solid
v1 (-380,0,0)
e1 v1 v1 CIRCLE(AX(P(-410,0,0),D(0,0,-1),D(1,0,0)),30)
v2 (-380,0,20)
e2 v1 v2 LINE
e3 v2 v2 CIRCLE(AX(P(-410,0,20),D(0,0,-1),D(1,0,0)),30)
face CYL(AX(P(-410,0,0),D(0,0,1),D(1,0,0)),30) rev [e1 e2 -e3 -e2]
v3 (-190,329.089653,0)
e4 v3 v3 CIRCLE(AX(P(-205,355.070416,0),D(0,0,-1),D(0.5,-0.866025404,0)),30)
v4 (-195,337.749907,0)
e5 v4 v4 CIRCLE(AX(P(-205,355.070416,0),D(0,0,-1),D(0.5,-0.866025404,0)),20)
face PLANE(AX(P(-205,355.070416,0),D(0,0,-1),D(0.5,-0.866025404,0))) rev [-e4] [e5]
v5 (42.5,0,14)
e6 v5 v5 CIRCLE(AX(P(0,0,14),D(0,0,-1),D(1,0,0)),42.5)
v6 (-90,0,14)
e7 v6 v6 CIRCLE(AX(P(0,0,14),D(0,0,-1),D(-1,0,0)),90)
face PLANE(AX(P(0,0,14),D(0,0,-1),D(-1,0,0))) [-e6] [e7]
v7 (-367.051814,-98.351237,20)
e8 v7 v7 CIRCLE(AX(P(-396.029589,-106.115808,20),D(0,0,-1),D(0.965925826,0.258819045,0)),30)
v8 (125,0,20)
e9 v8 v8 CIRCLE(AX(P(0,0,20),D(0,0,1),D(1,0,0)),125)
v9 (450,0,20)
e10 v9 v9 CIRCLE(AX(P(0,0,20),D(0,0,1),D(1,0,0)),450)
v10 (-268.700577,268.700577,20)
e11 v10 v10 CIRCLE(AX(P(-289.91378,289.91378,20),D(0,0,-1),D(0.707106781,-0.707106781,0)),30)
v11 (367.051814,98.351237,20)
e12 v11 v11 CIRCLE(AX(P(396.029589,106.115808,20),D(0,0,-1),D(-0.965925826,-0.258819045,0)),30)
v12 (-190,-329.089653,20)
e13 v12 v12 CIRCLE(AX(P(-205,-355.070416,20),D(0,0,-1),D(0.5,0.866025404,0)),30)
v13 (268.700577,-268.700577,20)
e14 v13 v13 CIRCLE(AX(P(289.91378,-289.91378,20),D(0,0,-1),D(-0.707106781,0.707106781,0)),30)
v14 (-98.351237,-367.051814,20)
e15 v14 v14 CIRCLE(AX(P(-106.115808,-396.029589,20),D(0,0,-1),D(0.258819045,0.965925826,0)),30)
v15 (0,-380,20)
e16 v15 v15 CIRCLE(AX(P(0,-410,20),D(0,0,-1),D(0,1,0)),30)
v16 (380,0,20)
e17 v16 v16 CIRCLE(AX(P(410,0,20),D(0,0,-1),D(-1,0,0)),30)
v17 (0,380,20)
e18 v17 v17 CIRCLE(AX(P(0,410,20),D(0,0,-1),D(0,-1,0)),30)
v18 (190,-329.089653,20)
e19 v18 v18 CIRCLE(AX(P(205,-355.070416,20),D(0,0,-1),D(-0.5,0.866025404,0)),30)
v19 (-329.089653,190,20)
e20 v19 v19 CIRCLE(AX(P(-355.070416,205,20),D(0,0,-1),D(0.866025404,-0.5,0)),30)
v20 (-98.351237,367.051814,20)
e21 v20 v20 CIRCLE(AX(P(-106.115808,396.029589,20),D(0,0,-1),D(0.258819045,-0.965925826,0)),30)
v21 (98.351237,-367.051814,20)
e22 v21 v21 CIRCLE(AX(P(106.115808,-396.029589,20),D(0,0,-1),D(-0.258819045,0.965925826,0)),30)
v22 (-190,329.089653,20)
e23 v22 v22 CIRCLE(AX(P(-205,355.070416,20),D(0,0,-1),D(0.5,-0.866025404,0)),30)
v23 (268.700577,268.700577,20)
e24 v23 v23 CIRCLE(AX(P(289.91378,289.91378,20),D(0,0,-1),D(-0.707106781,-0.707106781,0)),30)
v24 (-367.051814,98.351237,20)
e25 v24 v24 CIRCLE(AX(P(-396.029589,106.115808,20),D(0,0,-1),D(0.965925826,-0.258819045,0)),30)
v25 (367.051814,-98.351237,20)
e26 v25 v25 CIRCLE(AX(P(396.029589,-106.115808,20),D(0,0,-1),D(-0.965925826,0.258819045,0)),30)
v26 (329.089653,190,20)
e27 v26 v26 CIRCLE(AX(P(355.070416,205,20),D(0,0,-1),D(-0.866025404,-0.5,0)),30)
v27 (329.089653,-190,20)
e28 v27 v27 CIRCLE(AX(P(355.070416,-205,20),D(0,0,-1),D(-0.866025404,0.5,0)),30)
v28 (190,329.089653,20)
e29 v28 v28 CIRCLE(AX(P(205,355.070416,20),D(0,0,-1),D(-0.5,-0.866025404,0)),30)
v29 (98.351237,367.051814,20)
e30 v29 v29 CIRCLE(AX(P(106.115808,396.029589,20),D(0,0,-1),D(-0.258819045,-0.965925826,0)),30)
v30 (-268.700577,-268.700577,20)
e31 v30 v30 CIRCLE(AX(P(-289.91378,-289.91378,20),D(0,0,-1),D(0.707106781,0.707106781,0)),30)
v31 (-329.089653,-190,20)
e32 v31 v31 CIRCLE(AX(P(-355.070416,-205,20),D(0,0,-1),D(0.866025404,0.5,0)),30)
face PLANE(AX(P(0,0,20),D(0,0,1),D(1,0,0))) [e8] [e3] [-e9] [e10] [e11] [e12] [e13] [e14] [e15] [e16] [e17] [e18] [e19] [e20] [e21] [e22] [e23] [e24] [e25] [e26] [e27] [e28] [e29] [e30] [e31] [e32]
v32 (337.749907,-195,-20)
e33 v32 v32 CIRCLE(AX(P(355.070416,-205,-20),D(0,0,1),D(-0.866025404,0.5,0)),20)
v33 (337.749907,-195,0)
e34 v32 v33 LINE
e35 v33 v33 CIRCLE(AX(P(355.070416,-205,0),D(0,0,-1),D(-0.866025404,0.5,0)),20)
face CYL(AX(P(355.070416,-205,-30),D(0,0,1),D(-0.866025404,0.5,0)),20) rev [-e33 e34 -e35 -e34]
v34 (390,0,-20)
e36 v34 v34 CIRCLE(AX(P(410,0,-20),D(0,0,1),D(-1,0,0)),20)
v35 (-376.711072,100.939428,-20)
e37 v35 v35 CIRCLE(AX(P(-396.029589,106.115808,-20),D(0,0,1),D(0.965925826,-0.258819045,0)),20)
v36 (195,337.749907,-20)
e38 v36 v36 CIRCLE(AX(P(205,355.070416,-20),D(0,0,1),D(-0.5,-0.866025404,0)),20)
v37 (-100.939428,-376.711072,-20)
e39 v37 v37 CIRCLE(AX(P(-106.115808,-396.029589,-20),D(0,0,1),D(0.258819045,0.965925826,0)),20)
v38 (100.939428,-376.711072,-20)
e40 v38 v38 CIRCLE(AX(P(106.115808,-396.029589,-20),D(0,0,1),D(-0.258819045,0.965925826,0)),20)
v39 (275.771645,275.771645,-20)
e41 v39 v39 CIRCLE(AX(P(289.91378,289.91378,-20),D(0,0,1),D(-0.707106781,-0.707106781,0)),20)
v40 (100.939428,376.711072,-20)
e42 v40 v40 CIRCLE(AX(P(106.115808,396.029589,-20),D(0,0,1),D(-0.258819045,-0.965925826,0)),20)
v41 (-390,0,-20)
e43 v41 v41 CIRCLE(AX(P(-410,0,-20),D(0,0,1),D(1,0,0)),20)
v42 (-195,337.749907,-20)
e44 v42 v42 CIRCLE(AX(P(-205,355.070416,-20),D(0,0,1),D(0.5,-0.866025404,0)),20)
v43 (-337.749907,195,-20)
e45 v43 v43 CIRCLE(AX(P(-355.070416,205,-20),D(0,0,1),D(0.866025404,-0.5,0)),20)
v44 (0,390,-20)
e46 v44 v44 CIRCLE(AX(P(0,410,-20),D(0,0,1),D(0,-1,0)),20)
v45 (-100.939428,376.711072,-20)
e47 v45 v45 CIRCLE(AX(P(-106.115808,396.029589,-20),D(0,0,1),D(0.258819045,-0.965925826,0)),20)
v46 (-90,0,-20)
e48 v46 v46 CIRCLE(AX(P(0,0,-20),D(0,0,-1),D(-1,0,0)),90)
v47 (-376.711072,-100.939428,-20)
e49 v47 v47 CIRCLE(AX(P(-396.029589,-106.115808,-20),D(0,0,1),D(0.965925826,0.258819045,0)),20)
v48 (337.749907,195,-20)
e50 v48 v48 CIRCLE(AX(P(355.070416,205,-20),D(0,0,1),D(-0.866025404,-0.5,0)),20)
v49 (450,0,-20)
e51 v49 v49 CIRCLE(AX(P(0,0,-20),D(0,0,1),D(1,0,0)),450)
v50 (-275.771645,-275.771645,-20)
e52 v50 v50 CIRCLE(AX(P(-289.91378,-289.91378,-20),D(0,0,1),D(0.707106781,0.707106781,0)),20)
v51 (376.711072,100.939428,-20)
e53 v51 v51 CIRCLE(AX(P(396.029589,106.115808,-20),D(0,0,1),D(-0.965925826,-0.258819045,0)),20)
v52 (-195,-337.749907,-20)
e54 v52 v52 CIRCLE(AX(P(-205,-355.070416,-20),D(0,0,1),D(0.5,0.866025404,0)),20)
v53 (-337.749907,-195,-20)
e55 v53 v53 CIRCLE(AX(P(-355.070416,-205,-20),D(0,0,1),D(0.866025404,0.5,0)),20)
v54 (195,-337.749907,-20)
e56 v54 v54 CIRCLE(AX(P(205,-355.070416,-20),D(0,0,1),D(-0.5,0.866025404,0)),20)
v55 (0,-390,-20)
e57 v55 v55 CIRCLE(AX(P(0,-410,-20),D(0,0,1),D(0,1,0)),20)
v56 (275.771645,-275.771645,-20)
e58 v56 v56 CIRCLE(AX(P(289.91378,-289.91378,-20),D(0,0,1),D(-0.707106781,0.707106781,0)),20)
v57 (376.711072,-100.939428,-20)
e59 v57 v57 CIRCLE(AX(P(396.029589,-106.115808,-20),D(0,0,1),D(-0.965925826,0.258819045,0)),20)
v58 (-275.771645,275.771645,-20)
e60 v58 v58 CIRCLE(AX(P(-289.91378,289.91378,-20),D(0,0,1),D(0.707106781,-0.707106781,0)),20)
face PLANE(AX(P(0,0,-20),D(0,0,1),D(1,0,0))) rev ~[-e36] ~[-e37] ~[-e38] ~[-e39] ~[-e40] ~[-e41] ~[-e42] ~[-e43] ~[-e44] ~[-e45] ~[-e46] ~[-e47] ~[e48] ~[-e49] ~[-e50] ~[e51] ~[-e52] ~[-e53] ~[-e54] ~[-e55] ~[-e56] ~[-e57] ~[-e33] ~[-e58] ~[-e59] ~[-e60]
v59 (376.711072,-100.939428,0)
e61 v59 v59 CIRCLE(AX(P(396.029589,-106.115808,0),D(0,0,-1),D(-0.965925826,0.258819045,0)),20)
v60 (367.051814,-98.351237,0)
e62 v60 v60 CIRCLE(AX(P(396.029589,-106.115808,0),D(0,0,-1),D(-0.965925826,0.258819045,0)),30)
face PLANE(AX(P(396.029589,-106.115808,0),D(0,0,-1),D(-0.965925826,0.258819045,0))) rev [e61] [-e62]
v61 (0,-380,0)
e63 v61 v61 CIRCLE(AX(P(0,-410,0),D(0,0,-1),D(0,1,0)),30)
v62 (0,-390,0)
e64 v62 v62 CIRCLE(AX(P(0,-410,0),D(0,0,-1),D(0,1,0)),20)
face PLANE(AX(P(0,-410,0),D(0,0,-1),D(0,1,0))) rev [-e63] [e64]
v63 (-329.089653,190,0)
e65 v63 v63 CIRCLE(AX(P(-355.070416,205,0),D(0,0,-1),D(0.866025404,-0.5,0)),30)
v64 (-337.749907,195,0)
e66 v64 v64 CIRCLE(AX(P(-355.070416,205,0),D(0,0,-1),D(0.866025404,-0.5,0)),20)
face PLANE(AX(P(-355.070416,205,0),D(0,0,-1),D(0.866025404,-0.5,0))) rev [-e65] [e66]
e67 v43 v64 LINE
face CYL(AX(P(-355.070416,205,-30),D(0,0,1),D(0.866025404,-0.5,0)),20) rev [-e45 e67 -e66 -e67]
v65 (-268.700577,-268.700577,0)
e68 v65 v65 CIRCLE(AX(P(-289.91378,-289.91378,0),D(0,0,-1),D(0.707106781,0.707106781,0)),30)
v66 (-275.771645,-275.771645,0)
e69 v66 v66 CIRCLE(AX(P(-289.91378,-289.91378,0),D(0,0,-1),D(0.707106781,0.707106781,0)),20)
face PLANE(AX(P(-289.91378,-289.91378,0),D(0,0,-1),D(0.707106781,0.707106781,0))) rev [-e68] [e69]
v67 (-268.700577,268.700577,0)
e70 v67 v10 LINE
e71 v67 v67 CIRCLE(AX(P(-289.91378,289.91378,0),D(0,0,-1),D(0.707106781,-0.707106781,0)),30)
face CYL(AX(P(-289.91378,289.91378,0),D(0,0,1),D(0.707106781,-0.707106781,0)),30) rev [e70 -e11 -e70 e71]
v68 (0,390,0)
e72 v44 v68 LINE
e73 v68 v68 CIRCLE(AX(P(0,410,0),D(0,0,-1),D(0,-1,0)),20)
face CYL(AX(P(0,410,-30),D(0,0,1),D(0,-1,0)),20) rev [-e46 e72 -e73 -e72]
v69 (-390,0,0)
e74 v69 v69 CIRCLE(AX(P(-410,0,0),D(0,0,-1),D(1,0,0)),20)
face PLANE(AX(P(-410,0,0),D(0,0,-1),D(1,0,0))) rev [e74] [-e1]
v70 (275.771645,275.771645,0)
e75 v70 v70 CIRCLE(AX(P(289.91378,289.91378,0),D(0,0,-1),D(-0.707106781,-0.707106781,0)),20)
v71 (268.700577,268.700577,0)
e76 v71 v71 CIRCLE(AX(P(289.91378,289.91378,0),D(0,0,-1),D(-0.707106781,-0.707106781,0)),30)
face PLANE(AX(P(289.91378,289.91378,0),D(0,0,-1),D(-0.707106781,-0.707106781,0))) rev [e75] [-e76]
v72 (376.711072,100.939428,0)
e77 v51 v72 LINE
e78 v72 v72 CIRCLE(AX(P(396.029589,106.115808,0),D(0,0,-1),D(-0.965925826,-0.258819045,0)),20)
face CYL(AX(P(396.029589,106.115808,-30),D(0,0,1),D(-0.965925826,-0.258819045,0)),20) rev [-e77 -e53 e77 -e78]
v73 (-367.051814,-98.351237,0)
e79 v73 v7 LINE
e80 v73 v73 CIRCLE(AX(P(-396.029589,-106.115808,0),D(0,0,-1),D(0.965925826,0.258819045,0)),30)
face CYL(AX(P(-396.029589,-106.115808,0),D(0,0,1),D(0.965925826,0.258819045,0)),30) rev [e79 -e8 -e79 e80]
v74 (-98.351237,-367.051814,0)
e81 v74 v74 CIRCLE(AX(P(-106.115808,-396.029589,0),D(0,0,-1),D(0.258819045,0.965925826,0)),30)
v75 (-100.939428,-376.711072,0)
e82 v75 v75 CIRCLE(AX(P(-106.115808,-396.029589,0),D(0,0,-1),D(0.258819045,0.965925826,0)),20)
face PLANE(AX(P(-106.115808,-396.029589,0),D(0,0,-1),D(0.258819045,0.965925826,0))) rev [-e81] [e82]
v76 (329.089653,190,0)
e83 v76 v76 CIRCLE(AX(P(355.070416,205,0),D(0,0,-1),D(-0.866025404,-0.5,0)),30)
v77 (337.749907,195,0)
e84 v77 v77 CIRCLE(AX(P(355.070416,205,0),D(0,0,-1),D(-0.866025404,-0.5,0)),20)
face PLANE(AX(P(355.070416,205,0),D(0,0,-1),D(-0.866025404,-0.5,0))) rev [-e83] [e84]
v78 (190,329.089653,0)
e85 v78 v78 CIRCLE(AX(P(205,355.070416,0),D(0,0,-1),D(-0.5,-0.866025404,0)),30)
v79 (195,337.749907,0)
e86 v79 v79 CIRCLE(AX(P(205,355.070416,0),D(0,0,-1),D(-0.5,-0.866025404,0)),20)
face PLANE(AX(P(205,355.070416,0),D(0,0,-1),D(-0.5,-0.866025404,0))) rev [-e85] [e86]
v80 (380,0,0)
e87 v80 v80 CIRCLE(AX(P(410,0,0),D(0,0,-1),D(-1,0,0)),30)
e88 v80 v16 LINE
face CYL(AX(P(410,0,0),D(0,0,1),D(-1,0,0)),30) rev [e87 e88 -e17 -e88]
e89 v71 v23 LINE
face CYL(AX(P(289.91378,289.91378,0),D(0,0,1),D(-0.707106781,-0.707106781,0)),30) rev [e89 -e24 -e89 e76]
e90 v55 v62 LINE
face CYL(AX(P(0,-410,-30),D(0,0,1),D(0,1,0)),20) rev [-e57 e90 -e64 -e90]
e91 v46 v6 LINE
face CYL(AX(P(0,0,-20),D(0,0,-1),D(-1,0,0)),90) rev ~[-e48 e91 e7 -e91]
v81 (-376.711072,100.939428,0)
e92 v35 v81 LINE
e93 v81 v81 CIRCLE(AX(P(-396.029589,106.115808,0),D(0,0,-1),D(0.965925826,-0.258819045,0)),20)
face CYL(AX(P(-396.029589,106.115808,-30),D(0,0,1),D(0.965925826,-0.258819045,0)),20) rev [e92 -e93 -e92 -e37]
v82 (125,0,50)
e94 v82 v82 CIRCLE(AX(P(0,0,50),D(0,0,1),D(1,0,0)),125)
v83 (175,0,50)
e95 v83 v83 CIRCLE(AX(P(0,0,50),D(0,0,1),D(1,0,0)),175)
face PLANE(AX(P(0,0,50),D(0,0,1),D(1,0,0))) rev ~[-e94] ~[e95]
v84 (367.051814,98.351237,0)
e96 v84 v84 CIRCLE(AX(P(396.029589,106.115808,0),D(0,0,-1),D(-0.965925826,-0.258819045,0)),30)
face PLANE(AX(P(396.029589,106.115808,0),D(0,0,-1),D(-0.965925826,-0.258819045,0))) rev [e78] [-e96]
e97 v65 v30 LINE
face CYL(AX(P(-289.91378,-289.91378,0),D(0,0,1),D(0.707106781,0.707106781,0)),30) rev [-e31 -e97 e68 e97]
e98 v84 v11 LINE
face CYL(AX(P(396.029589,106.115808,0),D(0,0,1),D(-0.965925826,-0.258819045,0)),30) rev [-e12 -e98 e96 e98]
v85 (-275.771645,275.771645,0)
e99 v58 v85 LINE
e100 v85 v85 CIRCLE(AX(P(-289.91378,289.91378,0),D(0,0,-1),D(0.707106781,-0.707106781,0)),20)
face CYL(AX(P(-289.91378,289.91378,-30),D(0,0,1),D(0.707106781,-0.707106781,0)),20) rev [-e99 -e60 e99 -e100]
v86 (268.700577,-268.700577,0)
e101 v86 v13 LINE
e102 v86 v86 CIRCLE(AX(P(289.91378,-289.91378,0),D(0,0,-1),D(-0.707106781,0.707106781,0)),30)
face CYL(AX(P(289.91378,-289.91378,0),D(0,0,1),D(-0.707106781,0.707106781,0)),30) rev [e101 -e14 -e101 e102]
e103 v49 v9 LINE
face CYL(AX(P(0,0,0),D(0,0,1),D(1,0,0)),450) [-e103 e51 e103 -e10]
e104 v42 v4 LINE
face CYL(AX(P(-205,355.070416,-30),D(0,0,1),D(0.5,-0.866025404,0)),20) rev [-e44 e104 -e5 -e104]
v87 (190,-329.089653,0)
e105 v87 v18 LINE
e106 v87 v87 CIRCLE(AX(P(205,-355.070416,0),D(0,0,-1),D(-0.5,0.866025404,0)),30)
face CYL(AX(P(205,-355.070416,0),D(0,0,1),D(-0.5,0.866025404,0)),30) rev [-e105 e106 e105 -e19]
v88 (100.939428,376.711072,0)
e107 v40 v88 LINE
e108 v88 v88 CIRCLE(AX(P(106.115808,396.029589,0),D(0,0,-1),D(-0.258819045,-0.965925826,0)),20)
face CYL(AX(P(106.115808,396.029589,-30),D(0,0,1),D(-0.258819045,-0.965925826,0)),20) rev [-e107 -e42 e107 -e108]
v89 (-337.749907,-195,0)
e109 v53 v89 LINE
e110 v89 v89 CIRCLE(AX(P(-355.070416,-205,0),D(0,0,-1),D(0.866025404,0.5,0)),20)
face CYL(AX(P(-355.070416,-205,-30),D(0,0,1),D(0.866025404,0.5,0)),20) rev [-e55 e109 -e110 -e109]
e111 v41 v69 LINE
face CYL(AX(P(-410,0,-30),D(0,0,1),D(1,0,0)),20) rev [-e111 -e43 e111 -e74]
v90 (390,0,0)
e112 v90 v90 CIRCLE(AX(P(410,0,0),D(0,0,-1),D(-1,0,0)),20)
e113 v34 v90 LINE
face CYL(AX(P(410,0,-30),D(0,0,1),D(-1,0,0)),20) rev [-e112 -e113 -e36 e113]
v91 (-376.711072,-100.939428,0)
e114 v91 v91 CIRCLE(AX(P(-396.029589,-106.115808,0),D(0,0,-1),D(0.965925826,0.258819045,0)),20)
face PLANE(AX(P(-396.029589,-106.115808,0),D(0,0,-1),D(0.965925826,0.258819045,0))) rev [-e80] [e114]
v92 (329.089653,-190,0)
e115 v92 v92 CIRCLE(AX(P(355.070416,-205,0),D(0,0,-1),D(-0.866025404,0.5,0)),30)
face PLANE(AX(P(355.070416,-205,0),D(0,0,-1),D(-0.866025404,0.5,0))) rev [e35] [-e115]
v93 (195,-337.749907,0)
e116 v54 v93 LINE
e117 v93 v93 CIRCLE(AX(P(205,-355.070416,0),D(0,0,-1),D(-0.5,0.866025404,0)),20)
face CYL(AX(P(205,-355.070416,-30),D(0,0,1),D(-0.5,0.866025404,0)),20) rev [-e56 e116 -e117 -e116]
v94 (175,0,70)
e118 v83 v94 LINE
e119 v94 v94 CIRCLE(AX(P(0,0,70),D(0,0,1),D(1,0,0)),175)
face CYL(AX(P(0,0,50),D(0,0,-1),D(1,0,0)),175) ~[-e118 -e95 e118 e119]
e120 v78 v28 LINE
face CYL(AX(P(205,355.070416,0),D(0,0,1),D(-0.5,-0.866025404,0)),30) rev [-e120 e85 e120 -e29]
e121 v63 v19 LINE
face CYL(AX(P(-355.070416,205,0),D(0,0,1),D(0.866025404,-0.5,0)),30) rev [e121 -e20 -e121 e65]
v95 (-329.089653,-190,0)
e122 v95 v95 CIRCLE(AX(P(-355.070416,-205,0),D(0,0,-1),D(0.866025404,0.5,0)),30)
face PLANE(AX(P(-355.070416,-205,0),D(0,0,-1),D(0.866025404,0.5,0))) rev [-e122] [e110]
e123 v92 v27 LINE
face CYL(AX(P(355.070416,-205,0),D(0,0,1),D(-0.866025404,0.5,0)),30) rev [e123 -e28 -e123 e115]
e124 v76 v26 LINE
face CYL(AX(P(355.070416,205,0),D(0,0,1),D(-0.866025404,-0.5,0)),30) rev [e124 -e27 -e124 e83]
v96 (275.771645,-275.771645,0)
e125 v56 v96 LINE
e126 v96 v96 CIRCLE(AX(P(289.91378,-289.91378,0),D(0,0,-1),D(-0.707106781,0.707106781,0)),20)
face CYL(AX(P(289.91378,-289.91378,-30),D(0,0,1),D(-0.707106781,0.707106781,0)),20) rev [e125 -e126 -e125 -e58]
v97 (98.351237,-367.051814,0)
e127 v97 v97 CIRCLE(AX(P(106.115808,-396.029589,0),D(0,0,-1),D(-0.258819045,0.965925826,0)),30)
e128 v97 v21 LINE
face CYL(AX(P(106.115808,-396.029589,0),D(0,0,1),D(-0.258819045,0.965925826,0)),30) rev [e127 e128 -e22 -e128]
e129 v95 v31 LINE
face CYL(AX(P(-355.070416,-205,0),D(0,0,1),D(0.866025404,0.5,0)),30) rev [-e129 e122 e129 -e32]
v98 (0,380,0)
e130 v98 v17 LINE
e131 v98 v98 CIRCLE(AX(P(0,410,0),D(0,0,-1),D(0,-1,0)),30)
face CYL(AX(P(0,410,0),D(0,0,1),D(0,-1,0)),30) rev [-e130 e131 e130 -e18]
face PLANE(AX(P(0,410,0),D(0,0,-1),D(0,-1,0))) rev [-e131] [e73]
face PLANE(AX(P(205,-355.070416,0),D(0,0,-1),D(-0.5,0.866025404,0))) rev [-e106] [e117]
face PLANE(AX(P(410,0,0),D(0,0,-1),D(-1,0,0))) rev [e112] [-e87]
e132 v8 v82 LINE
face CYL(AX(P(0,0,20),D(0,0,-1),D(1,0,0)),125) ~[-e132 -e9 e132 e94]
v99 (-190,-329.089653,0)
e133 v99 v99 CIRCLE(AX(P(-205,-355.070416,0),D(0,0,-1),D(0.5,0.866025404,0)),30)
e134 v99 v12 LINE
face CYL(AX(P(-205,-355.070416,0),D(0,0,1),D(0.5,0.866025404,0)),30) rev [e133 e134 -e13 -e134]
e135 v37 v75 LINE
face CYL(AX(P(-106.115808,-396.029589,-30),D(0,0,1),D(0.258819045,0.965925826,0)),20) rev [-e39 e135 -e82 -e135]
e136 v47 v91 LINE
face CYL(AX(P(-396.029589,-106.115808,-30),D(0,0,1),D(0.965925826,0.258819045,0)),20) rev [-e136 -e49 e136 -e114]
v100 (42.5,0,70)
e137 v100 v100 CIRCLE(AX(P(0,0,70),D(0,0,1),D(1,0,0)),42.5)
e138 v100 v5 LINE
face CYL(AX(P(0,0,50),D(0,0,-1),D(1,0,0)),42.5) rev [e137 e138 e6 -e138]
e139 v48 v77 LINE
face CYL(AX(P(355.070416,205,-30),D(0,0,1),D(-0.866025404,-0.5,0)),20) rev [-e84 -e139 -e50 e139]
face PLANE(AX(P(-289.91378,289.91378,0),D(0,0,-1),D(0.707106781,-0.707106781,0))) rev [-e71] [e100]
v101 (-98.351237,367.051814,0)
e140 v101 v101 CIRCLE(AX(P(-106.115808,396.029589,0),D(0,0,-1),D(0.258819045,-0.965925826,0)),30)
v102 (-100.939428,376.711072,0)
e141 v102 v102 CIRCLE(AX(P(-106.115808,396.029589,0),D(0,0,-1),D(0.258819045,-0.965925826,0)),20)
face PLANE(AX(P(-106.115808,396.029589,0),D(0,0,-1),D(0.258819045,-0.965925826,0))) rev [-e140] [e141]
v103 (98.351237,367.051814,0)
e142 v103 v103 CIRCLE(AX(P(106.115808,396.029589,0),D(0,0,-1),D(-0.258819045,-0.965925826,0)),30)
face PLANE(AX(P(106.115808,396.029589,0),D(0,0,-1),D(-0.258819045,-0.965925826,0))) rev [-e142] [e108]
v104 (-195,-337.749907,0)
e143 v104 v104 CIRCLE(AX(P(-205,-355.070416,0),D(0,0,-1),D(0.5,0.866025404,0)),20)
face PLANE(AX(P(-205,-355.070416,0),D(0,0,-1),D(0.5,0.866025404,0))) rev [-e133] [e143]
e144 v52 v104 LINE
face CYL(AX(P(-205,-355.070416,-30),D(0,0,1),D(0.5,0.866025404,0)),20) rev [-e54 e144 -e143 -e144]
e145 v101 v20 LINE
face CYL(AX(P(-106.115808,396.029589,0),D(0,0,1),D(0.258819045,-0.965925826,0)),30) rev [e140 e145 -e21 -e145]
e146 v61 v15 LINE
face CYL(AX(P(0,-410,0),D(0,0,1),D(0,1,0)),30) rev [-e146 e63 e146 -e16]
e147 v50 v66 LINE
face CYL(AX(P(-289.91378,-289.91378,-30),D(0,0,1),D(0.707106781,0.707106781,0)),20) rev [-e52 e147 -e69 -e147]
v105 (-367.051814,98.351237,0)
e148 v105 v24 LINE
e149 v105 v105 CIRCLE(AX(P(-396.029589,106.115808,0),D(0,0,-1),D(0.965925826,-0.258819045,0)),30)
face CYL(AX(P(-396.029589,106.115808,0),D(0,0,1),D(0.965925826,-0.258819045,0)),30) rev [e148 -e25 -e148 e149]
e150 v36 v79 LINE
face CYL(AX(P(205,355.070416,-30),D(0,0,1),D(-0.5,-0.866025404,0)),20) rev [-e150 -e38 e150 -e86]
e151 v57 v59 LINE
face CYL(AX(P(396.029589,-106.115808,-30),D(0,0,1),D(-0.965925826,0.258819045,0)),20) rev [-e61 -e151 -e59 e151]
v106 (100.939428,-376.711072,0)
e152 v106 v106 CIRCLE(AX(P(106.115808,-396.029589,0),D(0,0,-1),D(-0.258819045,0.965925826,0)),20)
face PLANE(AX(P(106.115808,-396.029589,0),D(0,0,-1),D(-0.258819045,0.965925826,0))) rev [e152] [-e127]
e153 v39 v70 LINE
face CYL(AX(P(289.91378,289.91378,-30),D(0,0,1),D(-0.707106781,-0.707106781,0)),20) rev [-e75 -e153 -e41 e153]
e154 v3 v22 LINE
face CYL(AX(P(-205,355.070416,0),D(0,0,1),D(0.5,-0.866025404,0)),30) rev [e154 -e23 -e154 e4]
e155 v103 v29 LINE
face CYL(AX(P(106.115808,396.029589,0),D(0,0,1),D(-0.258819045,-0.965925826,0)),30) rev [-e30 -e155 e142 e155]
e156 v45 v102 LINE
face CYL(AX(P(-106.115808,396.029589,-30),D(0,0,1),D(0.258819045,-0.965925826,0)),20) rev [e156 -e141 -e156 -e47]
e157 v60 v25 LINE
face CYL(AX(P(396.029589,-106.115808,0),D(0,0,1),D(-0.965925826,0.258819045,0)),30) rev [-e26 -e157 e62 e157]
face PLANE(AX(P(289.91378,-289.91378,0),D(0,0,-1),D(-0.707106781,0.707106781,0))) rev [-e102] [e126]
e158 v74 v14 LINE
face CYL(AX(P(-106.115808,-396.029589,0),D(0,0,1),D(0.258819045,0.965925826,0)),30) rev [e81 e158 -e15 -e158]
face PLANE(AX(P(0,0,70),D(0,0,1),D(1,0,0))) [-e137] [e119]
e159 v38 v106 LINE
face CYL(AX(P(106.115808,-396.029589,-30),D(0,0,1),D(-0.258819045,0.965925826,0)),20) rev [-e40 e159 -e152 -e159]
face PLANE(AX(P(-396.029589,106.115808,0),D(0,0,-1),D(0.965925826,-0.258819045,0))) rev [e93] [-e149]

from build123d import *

# Parameters (mm, degrees)
SKETCH_1_R               = 450
SKETCH_1_R_2             = 42.5
EXTRUDE_1_DEPTH          = 20
PATTERN_CIRCULAR_1_COUNT = 24
SKETCH_7_R               = 125
SKETCH_7_R_2             = 42.5
EXTRUDE_2_DEPTH          = 30
SKETCH_8_R               = 175
SKETCH_8_R_2             = 42.5
EXTRUDE_3_DEPTH          = 20
SKETCH_9_R               = 90
CUT_EXTRUDE_1_DEPTH      = 34


with BuildPart() as part:
    # 草图1 → 凸台-拉伸1 (new, symmetric)
    with BuildSketch(Plane.XY):
        Circle(SKETCH_1_R)
        Circle(SKETCH_1_R_2, mode=Mode.SUBTRACT)
    extrude(amount=EXTRUDE_1_DEPTH, both=True)

    # 草图4 → M42 六角头螺栓的柱形沉头孔1 (revolve, cut)
    with BuildSketch(Plane(origin=(0, 410, 20), x_dir=(0, -1, 0), z_dir=(1, 0, 0))):
        Polygon((0, 0), (0, 62.017212381), (20, 50), (20, 20), (30, 20), (30, 0), align=None)
    hole_wizard_m42_1 = revolve(axis=Axis((0, 410, 26.35), (0, 0, -1)), mode=Mode.SUBTRACT)

    # 阵列(圆周)1: M42 六角头螺栓的柱形沉头孔1 ×24 about axis
    pattern_circular_1_axis = Axis((0, 0, 0), (0, 0, 1))
    for i in range(1, PATTERN_CIRCULAR_1_COUNT):
        add(hole_wizard_m42_1.rotate(pattern_circular_1_axis, i * 360 / PATTERN_CIRCULAR_1_COUNT), mode=Mode.SUBTRACT)

    # 草图7 → 凸台-拉伸2 (add)
    with BuildSketch(Plane.XY.offset(20)):
        Circle(SKETCH_7_R)
        Circle(SKETCH_7_R_2, mode=Mode.SUBTRACT)
    extrude(amount=EXTRUDE_2_DEPTH)

    # 草图8 → 凸台-拉伸3 (add)
    with BuildSketch(Plane.XY.offset(50)):
        Circle(SKETCH_8_R)
        Circle(SKETCH_8_R_2, mode=Mode.SUBTRACT)
    extrude(amount=EXTRUDE_3_DEPTH)

    # 草图9 → 切除-拉伸1 (cut)
    with BuildSketch(Plane(origin=(0, 0, -20), x_dir=(-1, 0, 0), z_dir=(0, 0, -1))):
        Circle(SKETCH_9_R)
    extrude(amount=-CUT_EXTRUDE_1_DEPTH, mode=Mode.SUBTRACT)


solid = part.part
